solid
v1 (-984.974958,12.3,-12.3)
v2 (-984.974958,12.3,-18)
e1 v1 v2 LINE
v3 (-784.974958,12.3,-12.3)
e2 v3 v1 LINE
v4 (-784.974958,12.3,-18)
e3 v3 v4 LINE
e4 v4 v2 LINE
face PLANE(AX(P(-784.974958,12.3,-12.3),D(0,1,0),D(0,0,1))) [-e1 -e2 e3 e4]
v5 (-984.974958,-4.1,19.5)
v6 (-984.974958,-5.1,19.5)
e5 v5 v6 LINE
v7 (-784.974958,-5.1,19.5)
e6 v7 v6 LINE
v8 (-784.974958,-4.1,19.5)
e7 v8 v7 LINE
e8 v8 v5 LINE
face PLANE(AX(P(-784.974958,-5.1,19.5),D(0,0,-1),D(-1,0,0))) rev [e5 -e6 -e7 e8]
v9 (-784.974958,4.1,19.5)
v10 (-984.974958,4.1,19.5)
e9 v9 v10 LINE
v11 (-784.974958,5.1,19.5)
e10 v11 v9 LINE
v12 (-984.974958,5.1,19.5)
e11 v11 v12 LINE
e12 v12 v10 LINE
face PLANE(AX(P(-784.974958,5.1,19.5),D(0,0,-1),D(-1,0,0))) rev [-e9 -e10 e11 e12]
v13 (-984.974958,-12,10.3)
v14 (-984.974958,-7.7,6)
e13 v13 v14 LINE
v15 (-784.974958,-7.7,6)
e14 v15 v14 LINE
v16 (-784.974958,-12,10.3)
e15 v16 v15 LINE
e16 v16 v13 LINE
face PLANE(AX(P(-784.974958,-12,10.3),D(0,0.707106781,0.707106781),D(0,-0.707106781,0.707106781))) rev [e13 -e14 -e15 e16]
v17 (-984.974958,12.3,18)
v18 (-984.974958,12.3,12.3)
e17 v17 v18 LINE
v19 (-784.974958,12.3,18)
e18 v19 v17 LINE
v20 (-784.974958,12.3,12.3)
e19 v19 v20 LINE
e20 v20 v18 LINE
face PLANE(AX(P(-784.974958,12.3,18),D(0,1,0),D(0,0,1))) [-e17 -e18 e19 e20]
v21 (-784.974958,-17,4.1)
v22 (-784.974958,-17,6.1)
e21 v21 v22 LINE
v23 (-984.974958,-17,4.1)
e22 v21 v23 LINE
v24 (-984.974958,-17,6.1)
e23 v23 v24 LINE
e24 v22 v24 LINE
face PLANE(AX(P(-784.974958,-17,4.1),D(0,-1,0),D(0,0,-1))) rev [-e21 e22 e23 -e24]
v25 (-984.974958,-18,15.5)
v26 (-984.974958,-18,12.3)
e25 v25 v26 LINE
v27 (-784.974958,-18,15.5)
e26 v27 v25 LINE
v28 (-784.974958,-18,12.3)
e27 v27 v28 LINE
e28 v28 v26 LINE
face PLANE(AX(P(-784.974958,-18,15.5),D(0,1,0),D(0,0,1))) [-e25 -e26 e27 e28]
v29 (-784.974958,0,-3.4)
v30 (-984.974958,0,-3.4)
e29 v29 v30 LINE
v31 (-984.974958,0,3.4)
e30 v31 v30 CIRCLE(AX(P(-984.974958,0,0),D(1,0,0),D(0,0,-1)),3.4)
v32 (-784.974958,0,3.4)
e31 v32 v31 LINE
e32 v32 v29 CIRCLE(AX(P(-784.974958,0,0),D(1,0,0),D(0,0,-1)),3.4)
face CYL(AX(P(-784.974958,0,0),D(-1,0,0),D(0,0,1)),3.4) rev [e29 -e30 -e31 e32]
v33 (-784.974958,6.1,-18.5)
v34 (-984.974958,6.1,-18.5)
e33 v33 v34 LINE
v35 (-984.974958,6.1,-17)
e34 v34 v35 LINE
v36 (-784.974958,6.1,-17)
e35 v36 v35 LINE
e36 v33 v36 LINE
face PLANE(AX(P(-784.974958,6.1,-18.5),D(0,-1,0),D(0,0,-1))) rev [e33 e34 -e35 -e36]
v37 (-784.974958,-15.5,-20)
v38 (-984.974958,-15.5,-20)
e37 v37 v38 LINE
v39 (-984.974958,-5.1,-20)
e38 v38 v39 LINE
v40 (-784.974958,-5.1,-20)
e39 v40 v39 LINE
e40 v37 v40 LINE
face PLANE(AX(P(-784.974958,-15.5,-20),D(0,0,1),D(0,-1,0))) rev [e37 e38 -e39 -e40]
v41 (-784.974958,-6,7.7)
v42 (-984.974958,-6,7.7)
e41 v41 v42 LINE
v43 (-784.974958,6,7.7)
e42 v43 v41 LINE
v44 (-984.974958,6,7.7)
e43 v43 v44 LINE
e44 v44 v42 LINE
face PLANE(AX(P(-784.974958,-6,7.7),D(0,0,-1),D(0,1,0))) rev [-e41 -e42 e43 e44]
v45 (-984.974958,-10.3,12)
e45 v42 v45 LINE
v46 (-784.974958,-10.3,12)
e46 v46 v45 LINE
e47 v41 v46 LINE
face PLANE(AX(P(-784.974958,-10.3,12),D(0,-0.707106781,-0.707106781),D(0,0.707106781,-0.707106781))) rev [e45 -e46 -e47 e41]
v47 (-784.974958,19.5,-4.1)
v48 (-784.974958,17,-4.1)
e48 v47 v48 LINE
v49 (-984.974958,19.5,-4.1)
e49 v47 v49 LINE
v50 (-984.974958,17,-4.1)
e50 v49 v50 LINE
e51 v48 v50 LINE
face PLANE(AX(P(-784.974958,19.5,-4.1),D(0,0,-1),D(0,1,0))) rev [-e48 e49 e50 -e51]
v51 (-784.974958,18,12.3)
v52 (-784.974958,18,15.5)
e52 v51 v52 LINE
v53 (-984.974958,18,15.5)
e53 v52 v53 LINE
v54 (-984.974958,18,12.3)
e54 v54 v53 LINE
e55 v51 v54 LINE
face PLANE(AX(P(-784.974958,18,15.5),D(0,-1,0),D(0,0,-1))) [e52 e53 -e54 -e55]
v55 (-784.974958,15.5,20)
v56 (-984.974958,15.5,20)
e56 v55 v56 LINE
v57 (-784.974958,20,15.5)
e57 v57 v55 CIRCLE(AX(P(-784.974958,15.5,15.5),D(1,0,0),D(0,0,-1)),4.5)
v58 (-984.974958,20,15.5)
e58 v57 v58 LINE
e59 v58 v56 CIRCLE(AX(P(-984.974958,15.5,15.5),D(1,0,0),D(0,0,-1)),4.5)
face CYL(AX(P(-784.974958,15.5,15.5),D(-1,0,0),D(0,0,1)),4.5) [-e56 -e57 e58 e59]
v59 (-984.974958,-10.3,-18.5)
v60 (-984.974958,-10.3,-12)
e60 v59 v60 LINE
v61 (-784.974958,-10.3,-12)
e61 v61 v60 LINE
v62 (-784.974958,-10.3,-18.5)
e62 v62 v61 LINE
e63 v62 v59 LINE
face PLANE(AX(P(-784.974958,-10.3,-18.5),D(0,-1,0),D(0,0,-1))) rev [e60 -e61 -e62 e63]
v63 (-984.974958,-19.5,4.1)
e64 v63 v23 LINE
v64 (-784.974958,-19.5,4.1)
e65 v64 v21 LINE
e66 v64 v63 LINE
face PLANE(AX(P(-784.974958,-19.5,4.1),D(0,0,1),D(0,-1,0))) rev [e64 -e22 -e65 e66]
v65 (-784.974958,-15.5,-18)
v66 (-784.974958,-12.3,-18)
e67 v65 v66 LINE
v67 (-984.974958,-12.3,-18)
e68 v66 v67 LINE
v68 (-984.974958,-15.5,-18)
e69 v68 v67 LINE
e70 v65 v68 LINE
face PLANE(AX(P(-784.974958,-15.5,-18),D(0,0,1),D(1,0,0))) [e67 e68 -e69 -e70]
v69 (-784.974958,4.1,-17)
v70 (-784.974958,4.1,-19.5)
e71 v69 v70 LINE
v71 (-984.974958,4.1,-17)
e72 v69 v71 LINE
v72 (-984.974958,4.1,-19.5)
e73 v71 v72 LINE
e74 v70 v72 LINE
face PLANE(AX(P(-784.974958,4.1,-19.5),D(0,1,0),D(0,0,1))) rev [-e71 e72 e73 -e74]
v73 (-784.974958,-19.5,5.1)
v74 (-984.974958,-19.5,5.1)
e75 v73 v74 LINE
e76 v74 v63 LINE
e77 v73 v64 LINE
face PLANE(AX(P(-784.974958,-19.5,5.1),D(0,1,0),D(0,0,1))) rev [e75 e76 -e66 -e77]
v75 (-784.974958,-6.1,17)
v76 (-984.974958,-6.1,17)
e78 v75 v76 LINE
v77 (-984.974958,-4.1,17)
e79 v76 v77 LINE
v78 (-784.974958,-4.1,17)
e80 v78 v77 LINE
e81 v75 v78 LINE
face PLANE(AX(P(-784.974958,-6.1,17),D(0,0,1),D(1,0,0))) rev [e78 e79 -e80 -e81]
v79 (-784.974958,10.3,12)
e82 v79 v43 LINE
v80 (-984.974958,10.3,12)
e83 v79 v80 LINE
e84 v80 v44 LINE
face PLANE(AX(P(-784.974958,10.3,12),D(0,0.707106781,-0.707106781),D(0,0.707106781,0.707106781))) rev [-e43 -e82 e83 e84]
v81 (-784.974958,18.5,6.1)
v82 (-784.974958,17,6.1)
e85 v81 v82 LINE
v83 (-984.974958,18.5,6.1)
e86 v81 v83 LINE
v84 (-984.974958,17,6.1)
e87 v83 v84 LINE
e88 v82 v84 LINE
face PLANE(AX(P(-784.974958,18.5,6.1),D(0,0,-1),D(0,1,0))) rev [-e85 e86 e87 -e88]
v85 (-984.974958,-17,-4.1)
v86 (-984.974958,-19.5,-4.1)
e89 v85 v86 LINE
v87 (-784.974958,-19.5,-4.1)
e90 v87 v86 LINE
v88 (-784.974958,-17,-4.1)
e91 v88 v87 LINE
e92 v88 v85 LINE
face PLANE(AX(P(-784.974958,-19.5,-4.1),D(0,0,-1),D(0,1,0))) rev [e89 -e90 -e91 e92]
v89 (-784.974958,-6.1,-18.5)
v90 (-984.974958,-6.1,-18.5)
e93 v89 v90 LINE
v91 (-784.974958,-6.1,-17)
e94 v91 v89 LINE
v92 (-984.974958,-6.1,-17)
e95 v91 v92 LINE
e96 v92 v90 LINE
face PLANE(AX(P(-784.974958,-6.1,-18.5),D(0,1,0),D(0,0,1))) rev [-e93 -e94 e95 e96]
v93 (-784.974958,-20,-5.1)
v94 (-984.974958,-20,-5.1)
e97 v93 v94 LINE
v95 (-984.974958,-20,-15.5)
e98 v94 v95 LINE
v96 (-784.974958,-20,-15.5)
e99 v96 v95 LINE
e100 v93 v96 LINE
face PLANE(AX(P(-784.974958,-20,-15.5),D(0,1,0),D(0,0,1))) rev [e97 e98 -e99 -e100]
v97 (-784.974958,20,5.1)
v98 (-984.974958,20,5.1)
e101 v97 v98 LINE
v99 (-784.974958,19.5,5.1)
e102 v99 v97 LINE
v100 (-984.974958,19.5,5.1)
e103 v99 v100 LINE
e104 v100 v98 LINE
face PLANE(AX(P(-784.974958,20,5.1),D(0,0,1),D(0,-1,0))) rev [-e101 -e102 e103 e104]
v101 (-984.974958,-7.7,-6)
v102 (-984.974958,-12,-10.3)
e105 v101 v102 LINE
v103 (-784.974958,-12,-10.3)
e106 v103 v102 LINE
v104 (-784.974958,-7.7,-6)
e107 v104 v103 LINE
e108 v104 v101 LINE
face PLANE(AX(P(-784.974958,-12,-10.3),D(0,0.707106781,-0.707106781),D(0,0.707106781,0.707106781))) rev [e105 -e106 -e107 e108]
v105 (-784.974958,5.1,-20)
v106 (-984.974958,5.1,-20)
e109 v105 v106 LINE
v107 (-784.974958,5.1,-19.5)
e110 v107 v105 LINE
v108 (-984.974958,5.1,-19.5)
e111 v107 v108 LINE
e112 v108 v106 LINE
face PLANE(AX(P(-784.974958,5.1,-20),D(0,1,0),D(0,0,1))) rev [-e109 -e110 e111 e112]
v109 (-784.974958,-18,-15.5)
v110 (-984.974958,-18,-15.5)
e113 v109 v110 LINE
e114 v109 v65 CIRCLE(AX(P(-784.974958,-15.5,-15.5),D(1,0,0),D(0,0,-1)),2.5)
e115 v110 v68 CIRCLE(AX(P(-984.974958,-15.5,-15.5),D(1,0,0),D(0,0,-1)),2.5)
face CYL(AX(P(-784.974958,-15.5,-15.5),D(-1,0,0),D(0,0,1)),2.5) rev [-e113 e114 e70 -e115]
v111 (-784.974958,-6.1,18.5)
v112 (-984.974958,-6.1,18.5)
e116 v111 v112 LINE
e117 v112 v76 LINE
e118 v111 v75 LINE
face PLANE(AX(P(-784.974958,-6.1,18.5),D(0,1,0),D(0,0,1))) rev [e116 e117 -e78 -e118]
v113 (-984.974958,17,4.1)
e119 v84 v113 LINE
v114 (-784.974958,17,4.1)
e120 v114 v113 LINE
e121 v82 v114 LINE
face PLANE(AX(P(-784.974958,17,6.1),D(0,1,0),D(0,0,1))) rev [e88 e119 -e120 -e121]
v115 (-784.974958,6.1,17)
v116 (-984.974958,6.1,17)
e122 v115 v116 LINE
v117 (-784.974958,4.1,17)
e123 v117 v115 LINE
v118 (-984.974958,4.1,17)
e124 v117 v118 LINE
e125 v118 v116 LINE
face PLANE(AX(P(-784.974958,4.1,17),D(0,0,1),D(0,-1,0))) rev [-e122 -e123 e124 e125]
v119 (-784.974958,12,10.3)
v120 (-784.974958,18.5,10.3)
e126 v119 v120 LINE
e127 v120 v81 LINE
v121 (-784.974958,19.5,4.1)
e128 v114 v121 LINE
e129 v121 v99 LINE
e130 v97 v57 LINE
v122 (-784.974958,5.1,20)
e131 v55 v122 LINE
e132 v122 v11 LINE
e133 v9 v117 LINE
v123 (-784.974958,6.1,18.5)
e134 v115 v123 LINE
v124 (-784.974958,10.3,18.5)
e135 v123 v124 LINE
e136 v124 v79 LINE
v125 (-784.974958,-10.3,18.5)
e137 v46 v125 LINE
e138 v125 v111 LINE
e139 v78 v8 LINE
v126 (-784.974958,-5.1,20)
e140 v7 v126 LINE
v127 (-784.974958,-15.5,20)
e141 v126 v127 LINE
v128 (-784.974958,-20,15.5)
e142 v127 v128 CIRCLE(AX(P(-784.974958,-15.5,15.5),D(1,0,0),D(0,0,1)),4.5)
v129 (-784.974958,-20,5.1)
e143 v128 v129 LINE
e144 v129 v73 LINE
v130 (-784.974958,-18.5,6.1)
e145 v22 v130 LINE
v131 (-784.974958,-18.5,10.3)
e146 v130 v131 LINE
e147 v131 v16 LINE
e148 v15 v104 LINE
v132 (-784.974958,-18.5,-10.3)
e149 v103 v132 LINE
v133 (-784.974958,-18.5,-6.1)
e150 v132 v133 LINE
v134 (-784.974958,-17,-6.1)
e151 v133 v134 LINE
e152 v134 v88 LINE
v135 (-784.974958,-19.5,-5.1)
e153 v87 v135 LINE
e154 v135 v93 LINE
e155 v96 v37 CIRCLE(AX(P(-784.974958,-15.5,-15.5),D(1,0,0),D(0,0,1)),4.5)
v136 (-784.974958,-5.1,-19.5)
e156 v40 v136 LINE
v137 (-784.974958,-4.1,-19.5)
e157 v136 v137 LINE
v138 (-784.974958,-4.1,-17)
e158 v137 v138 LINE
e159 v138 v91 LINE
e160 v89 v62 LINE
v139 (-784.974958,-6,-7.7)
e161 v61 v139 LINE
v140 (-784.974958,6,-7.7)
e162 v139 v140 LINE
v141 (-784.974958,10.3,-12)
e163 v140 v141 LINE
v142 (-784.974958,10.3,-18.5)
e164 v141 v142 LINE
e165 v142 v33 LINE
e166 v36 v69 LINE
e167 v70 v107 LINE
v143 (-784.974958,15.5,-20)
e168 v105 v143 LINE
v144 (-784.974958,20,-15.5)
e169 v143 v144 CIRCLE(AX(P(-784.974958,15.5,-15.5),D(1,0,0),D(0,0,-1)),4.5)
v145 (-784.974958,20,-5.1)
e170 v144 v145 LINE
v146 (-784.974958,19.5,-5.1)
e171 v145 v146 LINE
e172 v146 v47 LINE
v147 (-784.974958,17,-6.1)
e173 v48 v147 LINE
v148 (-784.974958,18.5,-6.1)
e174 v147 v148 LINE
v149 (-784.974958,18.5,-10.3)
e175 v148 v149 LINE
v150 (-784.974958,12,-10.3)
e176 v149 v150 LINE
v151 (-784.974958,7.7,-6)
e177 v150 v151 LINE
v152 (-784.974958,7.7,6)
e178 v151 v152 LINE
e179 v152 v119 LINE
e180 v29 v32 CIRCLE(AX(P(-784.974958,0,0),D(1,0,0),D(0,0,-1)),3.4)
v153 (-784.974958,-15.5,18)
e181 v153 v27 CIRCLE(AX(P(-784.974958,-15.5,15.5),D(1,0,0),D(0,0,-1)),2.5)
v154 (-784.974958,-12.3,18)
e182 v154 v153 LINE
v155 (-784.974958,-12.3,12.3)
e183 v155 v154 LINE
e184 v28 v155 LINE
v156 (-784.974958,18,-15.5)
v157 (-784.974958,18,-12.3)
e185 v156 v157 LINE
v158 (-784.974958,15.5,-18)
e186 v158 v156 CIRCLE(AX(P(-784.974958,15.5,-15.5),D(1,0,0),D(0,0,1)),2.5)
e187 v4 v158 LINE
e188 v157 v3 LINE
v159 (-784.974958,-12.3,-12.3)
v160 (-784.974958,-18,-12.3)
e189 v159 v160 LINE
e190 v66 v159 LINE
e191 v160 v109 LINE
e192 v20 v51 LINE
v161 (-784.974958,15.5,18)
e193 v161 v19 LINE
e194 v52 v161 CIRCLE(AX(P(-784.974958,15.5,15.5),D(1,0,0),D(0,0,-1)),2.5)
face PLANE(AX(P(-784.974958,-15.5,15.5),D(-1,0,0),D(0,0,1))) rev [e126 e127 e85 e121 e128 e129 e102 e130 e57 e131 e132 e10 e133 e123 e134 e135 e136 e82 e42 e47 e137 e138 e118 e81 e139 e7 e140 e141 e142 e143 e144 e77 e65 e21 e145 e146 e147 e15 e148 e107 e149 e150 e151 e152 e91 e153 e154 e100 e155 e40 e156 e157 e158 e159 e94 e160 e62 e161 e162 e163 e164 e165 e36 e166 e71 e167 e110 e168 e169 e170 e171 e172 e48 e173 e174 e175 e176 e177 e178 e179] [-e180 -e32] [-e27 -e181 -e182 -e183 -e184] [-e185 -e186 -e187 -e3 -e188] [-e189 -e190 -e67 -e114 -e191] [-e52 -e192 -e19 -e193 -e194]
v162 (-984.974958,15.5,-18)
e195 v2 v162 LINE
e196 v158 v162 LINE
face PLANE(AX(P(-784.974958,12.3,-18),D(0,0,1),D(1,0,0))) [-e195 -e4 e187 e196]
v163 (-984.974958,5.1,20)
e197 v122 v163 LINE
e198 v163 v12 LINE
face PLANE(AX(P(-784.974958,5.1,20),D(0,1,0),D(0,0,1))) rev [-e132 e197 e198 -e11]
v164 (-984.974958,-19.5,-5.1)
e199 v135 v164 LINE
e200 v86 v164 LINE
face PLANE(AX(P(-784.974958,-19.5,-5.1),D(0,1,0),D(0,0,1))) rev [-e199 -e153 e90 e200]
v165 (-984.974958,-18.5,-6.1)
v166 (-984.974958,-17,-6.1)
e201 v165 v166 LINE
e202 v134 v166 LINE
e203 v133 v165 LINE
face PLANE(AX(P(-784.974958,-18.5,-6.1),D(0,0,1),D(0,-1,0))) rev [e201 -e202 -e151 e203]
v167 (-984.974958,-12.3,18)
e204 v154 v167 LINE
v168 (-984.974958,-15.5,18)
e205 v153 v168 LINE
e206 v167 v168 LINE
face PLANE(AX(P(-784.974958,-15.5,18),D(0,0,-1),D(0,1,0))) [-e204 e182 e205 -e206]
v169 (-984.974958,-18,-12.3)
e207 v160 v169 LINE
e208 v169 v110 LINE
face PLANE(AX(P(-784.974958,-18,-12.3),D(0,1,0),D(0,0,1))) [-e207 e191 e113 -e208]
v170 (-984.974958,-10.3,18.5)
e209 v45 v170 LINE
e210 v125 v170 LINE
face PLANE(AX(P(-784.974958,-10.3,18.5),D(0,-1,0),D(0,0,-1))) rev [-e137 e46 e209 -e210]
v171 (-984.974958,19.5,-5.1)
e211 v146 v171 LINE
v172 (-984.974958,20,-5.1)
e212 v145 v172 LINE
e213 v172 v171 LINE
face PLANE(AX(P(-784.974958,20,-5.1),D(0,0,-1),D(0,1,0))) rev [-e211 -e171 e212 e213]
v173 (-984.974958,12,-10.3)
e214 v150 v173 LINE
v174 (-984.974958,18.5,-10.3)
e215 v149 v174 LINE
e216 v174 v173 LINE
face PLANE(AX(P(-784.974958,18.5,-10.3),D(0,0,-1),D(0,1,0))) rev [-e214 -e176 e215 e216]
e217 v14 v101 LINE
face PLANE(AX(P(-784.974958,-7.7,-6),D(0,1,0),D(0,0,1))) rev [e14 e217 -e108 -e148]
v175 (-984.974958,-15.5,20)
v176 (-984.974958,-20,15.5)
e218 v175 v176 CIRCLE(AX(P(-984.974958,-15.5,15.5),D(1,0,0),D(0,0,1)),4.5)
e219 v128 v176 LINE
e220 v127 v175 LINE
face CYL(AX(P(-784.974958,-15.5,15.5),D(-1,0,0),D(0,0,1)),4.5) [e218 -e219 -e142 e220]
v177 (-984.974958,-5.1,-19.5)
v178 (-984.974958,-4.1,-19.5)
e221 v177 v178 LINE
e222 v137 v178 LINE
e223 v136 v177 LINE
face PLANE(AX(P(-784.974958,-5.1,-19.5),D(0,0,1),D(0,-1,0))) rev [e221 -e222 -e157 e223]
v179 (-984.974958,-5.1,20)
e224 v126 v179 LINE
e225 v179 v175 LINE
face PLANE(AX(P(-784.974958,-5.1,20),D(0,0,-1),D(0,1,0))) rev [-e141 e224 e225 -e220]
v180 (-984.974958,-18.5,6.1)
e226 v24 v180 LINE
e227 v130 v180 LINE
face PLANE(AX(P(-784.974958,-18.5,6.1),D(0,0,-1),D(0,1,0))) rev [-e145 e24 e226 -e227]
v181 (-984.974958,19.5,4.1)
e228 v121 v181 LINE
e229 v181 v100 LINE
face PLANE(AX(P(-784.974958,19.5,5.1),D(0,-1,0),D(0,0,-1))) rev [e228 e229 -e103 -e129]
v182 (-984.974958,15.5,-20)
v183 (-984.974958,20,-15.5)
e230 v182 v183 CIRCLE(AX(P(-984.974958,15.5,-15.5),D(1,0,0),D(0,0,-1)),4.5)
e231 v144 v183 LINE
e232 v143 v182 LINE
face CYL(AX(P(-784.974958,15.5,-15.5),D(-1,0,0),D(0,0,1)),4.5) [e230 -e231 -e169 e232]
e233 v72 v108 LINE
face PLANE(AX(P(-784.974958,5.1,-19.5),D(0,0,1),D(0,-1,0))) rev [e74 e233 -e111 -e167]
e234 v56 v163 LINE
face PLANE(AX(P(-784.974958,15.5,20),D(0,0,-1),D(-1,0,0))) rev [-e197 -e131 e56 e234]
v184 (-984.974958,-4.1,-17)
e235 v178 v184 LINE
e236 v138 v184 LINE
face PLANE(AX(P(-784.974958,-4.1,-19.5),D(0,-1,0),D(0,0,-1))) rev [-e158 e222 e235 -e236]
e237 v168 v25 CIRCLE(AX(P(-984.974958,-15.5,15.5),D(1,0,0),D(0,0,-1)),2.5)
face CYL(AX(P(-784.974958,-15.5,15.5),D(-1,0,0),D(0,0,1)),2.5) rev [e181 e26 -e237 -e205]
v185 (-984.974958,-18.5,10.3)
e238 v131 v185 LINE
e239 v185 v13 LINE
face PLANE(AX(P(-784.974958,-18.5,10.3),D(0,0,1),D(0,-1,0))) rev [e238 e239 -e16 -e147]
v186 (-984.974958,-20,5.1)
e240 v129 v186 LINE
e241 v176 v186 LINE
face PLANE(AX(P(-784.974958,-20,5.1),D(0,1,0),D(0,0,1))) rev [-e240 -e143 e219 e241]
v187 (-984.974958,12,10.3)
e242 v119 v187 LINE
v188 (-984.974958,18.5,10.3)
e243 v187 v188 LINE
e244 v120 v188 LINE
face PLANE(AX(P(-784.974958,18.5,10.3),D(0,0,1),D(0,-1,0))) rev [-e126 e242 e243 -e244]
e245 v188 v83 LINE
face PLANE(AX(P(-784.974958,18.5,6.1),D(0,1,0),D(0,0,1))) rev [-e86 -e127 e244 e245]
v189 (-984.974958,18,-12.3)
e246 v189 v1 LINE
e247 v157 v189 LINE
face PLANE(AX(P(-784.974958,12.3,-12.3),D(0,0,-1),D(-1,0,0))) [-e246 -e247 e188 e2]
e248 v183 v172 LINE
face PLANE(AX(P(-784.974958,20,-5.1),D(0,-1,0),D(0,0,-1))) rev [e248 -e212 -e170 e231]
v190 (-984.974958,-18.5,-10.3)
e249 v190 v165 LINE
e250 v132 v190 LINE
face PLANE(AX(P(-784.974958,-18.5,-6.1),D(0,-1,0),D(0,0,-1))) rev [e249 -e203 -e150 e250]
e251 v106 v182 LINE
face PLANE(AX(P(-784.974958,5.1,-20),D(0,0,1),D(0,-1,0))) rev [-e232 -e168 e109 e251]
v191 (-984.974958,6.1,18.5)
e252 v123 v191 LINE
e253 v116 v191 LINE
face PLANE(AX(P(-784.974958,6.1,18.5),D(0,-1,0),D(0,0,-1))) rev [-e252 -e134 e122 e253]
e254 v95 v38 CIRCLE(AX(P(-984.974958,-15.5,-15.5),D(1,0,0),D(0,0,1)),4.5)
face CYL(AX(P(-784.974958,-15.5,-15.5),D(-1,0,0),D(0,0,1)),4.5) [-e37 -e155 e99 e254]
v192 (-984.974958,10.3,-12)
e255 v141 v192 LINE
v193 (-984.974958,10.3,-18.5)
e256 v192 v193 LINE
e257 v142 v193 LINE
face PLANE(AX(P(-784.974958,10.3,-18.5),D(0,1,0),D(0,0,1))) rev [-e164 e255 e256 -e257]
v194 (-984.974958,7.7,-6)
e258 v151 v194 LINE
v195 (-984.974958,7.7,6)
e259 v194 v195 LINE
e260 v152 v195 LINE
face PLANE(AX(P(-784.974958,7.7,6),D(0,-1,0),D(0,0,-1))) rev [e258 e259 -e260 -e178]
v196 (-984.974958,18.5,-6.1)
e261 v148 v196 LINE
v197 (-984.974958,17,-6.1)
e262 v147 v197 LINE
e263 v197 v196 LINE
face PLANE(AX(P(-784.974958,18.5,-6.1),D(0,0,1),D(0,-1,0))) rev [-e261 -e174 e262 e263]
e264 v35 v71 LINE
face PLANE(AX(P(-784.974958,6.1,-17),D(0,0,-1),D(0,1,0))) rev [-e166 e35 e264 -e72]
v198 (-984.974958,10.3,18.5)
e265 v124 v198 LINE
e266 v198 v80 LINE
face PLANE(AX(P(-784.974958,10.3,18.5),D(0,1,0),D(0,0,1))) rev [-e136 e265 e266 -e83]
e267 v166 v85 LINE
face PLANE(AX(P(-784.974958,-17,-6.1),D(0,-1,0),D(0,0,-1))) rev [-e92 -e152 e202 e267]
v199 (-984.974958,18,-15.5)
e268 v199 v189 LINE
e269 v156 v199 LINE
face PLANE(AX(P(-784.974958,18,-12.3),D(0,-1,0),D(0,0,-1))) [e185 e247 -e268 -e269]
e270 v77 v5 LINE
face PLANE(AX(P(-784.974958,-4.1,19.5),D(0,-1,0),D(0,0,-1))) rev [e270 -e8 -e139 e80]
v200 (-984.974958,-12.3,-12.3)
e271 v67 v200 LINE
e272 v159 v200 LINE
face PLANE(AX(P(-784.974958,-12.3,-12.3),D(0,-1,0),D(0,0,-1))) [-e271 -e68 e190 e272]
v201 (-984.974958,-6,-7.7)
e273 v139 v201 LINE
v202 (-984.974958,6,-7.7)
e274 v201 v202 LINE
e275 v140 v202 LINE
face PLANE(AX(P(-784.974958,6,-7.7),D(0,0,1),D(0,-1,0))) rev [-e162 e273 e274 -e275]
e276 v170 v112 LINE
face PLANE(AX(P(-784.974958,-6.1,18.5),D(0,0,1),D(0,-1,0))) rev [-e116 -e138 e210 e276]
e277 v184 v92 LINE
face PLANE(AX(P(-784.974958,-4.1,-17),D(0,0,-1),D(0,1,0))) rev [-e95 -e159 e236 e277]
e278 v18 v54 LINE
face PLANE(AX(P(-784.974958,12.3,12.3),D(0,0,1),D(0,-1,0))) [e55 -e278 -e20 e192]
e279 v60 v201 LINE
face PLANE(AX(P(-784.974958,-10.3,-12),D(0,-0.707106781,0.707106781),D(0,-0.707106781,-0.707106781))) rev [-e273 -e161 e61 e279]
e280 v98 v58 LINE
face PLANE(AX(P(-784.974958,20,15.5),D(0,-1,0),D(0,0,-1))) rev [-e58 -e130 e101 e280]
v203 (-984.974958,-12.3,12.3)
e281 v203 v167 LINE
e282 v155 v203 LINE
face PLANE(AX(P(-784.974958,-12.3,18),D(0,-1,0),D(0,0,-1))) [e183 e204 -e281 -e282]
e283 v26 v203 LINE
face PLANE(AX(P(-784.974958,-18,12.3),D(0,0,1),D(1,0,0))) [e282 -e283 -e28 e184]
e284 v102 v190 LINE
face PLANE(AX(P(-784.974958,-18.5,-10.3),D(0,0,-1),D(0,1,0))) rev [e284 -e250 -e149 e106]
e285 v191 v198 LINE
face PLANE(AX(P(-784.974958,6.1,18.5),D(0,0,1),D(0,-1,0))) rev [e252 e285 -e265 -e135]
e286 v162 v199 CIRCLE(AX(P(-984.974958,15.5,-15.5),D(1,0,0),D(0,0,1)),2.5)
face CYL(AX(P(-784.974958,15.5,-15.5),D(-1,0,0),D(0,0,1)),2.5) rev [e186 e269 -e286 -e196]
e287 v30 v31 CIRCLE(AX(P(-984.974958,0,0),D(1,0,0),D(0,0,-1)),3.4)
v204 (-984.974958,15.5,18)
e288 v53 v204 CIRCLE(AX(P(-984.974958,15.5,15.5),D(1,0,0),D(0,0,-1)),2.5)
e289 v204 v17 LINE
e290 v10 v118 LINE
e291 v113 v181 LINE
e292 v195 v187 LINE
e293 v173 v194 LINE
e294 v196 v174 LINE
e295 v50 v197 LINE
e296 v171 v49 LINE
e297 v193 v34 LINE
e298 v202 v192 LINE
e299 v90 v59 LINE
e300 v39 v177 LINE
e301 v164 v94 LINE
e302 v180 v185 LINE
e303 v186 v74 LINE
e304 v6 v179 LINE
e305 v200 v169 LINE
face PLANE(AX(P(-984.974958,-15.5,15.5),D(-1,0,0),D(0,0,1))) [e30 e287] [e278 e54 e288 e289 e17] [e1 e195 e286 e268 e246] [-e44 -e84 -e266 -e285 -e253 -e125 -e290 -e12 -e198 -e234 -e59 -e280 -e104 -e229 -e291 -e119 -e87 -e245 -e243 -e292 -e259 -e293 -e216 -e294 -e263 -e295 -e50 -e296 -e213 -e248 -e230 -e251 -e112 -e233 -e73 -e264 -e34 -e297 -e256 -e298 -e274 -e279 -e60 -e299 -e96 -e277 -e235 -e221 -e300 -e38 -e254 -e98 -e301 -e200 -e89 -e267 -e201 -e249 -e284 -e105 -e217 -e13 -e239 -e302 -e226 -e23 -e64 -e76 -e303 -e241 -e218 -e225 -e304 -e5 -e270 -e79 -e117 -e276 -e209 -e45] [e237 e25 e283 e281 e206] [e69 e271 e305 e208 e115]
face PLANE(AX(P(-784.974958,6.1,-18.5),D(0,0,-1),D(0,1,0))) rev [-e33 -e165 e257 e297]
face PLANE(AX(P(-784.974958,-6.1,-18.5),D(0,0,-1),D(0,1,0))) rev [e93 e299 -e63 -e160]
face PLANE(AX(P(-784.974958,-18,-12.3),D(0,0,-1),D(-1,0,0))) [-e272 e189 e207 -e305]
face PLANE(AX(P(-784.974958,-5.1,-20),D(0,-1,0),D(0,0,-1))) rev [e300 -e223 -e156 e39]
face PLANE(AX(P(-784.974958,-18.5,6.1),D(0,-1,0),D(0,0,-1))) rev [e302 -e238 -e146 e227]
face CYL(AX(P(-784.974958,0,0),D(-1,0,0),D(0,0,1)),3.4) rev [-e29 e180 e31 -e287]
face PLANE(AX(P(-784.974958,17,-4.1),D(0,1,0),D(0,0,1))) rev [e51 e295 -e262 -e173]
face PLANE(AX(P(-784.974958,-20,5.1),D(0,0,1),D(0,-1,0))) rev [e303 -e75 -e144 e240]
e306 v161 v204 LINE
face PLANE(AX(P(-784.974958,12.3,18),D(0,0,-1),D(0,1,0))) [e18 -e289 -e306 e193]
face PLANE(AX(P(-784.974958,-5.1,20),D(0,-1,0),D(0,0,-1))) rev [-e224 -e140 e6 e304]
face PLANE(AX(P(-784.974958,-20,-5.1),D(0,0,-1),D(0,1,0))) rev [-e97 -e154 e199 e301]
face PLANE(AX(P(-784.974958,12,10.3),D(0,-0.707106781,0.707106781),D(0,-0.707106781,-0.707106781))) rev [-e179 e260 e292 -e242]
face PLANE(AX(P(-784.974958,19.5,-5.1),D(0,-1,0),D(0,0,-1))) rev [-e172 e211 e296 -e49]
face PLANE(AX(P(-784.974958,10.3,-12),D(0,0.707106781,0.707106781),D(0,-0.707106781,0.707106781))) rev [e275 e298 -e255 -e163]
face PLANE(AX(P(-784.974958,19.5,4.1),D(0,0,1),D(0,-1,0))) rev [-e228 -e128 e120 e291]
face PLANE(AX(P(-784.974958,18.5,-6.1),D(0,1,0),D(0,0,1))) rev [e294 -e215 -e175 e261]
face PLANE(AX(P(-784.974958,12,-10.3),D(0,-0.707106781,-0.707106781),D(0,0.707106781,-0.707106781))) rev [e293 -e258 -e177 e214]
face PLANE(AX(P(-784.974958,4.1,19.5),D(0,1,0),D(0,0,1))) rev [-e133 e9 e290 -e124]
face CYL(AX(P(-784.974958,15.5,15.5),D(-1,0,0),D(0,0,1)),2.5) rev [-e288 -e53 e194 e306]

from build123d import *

# Parameters (mm, degrees)
SKETCH1_R                                 = 3.4
ALUMINIUM_PROFILE_40_X_40B_X_R4_5_1_DEPTH = 200


with BuildPart() as part:
    # Sketch1 → Aluminium profile 40 X 40B X R4.5(1) (new body)
    with BuildSketch(Plane.YZ.offset(-984.974958264)):
        with BuildLine():
            Line((-5.1, 20), (-5.1, 19.5))
            Line((-5.1, 19.5), (-4.1, 19.5))
            Line((-4.1, 19.5), (-4.1, 17))
            Line((-4.1, 17), (-6.1, 17))
            Line((-6.1, 17), (-6.1, 18.5))
            Line((-6.1, 18.5), (-10.3, 18.5))
            Line((-10.3, 18.5), (-10.3, 12))
            Line((-10.3, 12), (-6, 7.7))
            Line((-6, 7.7), (6, 7.7))
            Line((6, 7.7), (10.3, 12))
            Line((10.3, 12), (10.3, 18.5))
            Line((10.3, 18.5), (6.1, 18.5))
            Line((6.1, 18.5), (6.1, 17))
            Line((6.1, 17), (4.1, 17))
            Line((4.1, 17), (4.1, 19.5))
            Line((4.1, 19.5), (5.1, 19.5))
            Line((5.1, 19.5), (5.1, 20))
            Line((5.1, 20), (15.5, 20))
            ThreePointArc((15.5, 20), (18.681980515, 18.681980515), (20, 15.5))
            Line((20, 15.5), (20, 5.1))
            Line((20, 5.1), (19.5, 5.1))
            Line((19.5, 5.1), (19.5, 4.1))
            Line((19.5, 4.1), (17, 4.1))
            Line((17, 4.1), (17, 6.1))
            Line((17, 6.1), (18.5, 6.1))
            Line((18.5, 6.1), (18.5, 10.3))
            Line((18.5, 10.3), (12, 10.3))
            Line((12, 10.3), (7.7, 6))
            Line((7.7, 6), (7.7, -6))
            Line((7.7, -6), (12, -10.3))
            Line((12, -10.3), (18.5, -10.3))
            Line((18.5, -10.3), (18.5, -6.1))
            Line((18.5, -6.1), (17, -6.1))
            Line((17, -6.1), (17, -4.1))
            Line((17, -4.1), (19.5, -4.1))
            Line((19.5, -4.1), (19.5, -5.1))
            Line((19.5, -5.1), (20, -5.1))
            Line((20, -5.1), (20, -15.5))
            ThreePointArc((20, -15.5), (18.681980515, -18.681980515), (15.5, -20))
            Line((15.5, -20), (5.1, -20))
            Line((5.1, -20), (5.1, -19.5))
            Line((5.1, -19.5), (4.1, -19.5))
            Line((4.1, -19.5), (4.1, -17))
            Line((4.1, -17), (6.1, -17))
            Line((6.1, -17), (6.1, -18.5))
            Line((6.1, -18.5), (10.3, -18.5))
            Line((10.3, -18.5), (10.3, -12))
            Line((10.3, -12), (6, -7.7))
            Line((6, -7.7), (-6, -7.7))
            Line((-6, -7.7), (-10.3, -12))
            Line((-10.3, -12), (-10.3, -18.5))
            Line((-10.3, -18.5), (-6.1, -18.5))
            Line((-6.1, -18.5), (-6.1, -17))
            Line((-6.1, -17), (-4.1, -17))
            Line((-4.1, -17), (-4.1, -19.5))
            Line((-4.1, -19.5), (-5.1, -19.5))
            Line((-5.1, -19.5), (-5.1, -20))
            Line((-5.1, -20), (-15.5, -20))
            ThreePointArc((-15.5, -20), (-18.681980515, -18.681980515), (-20, -15.5))
            Line((-20, -15.5), (-20, -5.1))
            Line((-20, -5.1), (-19.5, -5.1))
            Line((-19.5, -5.1), (-19.5, -4.1))
            Line((-19.5, -4.1), (-17, -4.1))
            Line((-17, -4.1), (-17, -6.1))
            Line((-17, -6.1), (-18.5, -6.1))
            Line((-18.5, -6.1), (-18.5, -10.3))
            Line((-18.5, -10.3), (-12, -10.3))
            Line((-12, -10.3), (-7.7, -6))
            Line((-7.7, -6), (-7.7, 6))
            Line((-7.7, 6), (-12, 10.3))
            Line((-12, 10.3), (-18.5, 10.3))
            Line((-18.5, 10.3), (-18.5, 6.1))
            Line((-18.5, 6.1), (-17, 6.1))
            Line((-17, 6.1), (-17, 4.1))
            Line((-17, 4.1), (-19.5, 4.1))
            Line((-19.5, 4.1), (-19.5, 5.1))
            Line((-19.5, 5.1), (-20, 5.1))
            Line((-20, 5.1), (-20, 15.5))
            ThreePointArc((-20, 15.5), (-18.681980515, 18.681980515), (-15.5, 20))
            Line((-15.5, 20), (-5.1, 20))
        make_face()
        Circle(SKETCH1_R, mode=Mode.SUBTRACT)
        with BuildLine():
            Line((12.3, 18), (15.5, 18))
            ThreePointArc((15.5, 18), (17.267766953, 17.267766953), (18, 15.5))
            Line((18, 15.5), (18, 12.3))
            Line((18, 12.3), (12.3, 12.3))
            Line((12.3, 12.3), (12.3, 18))
        make_face(mode=Mode.SUBTRACT)
        with BuildLine():
            Line((-15.5, 18), (-12.3, 18))
            Line((-12.3, 18), (-12.3, 12.3))
            Line((-12.3, 12.3), (-18, 12.3))
            Line((-18, 12.3), (-18, 15.5))
            ThreePointArc((-18, 15.5), (-17.267766953, 17.267766953), (-15.5, 18))
        make_face(mode=Mode.SUBTRACT)
        with BuildLine():
            Line((-18, -12.3), (-12.3, -12.3))
            Line((-12.3, -12.3), (-12.3, -18))
            Line((-12.3, -18), (-15.5, -18))
            ThreePointArc((-15.5, -18), (-17.267766953, -17.267766953), (-18, -15.5))
            Line((-18, -15.5), (-18, -12.3))
        make_face(mode=Mode.SUBTRACT)
        with BuildLine():
            Line((12.3, -12.3), (18, -12.3))
            Line((18, -12.3), (18, -15.5))
            ThreePointArc((18, -15.5), (17.267766953, -17.267766953), (15.5, -18))
            Line((15.5, -18), (12.3, -18))
            Line((12.3, -18), (12.3, -12.3))
        make_face(mode=Mode.SUBTRACT)
    extrude(amount=ALUMINIUM_PROFILE_40_X_40B_X_R4_5_1_DEPTH)


solid = part.part
